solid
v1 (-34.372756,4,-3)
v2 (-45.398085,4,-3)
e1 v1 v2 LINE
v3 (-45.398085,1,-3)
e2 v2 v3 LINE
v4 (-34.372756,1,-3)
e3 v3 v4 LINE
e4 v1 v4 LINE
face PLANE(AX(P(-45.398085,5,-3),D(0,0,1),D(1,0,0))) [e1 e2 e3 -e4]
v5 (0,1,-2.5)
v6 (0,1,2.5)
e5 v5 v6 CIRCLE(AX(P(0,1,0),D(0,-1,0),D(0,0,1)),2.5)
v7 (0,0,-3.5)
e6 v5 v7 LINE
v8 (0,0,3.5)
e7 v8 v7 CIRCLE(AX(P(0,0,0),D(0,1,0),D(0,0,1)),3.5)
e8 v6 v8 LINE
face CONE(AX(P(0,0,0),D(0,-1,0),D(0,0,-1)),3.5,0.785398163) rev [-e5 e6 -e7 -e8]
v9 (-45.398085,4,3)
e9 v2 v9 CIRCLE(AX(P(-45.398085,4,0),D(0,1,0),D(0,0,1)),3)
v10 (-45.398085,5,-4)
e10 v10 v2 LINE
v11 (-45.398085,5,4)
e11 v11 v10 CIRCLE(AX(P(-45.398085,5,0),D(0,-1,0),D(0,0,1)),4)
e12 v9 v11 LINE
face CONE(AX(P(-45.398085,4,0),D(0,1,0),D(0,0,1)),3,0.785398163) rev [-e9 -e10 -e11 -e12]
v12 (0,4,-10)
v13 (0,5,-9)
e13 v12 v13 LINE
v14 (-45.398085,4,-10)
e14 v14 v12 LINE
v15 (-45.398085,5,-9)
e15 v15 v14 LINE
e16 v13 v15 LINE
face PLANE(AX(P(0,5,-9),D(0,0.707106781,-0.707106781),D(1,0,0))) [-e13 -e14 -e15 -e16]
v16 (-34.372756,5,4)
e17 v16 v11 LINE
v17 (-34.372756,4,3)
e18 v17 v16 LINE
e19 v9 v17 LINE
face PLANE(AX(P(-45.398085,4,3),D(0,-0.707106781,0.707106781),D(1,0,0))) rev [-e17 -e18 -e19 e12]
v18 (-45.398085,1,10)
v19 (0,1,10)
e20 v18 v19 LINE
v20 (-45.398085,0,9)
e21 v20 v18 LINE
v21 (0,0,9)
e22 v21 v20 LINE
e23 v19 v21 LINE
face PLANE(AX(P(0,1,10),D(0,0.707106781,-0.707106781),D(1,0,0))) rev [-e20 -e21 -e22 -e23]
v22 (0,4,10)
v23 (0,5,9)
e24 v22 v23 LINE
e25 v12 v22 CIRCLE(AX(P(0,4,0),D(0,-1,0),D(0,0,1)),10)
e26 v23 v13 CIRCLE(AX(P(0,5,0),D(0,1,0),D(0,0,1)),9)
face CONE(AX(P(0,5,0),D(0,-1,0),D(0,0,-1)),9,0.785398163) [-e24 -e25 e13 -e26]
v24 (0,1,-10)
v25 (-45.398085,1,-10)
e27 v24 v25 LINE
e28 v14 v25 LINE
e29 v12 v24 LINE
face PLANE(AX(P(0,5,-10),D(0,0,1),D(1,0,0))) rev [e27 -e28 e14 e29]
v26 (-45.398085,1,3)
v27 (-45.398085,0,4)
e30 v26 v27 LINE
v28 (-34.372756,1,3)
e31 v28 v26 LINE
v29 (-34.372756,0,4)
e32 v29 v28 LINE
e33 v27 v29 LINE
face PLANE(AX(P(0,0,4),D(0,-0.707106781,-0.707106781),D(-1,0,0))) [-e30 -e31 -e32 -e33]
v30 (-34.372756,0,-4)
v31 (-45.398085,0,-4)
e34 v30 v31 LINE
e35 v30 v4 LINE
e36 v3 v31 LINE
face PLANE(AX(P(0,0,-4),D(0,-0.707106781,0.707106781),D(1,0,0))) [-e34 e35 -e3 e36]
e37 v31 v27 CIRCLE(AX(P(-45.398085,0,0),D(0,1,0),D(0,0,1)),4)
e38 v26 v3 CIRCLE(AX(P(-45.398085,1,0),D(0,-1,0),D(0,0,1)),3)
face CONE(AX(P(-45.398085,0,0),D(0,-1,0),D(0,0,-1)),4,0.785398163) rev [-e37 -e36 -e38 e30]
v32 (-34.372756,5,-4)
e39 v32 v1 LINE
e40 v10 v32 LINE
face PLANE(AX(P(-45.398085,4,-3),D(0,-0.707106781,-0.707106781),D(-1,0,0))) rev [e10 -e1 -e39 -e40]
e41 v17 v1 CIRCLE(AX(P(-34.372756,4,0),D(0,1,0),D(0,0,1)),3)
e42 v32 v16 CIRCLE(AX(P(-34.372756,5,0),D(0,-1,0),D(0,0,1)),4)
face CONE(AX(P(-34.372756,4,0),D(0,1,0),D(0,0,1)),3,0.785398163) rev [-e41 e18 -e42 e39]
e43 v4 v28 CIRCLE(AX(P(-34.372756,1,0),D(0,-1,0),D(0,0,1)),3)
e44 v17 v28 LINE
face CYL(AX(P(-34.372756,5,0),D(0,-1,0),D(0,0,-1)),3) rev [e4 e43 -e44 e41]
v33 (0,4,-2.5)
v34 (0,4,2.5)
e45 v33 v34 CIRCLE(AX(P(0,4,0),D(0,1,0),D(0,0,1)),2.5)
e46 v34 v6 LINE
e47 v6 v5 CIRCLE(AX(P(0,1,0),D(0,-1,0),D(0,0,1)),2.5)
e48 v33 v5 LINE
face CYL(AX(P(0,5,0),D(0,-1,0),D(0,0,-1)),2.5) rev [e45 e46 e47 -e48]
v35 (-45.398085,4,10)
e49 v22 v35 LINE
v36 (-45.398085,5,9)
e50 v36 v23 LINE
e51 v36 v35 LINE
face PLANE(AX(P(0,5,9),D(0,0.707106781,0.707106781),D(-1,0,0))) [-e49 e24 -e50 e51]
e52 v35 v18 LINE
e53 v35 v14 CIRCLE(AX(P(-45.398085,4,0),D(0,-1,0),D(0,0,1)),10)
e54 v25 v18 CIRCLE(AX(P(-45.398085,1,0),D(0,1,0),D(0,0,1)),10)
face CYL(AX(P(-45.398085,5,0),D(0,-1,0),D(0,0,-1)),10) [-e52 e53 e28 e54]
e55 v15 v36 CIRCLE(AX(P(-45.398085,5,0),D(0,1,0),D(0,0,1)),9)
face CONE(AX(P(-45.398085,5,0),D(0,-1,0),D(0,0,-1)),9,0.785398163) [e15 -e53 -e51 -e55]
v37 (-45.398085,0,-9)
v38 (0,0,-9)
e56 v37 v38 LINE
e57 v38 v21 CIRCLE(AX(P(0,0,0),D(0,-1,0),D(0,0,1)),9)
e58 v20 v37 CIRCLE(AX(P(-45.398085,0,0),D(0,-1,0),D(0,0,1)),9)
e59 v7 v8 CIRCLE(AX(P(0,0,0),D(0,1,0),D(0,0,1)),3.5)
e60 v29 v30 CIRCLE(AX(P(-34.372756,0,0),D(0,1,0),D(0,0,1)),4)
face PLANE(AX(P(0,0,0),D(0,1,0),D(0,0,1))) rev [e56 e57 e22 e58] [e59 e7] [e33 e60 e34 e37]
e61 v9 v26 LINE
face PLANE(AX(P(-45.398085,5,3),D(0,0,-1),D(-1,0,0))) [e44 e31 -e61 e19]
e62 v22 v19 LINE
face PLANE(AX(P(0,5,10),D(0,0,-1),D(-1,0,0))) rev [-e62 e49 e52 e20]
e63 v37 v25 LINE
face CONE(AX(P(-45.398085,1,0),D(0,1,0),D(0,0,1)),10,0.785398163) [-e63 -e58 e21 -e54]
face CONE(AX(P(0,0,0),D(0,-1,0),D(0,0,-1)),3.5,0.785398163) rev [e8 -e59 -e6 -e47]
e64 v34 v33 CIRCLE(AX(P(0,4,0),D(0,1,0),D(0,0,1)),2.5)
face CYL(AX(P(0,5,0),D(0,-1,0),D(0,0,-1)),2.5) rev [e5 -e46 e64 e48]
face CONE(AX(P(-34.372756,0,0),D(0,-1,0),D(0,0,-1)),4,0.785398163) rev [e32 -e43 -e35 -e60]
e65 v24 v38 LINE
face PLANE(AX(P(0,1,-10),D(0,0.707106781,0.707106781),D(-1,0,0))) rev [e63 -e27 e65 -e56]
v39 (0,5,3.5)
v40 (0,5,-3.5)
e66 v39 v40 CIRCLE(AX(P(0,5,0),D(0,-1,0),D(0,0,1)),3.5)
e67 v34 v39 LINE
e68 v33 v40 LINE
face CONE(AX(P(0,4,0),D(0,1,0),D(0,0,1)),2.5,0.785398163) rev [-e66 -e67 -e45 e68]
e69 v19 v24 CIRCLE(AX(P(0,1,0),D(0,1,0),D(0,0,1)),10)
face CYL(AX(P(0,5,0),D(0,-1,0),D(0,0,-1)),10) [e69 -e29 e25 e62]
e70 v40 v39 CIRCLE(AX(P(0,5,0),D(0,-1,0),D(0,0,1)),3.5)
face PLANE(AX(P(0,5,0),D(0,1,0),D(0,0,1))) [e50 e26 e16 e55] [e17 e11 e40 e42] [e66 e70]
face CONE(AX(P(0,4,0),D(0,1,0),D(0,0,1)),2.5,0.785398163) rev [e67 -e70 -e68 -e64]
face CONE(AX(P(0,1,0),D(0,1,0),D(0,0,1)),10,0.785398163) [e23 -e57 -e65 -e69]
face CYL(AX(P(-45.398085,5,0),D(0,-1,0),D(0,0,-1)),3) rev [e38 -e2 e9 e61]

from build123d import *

# Parameters (mm, degrees)
SKETCH1_R           = 2.5
BOSS_EXTRUDE1_DEPTH = 5
CHAMFER1_SIZE       = 1


with BuildPart() as part:
    # Sketch1 → Boss-Extrude1 (new body)
    with BuildSketch(Plane(origin=(0, 0, 0), x_dir=(1, 0, 0), z_dir=(0, 1, 0))):
        with BuildLine():
            Line((0, -10), (-45.398085341, -10))
            ThreePointArc((-45.398085341, -10), (-55.398085341, 0), (-45.398085341, 10))
            Line((-45.398085341, 10), (0, 10))
            ThreePointArc((0, 10), (10, 0), (0, -10))
        make_face()
        with Locations(Location((0, 0, 0), (0, 0, 270))):
            Circle(SKETCH1_R, mode=Mode.SUBTRACT)
        with BuildLine():
            Line((-45.398085341, 3), (-34.372756479, 3))
            ThreePointArc((-34.372756479, 3), (-31.372756479, 0), (-34.372756479, -3))
            Line((-34.372756479, -3), (-45.398085341, -3))
            ThreePointArc((-45.398085341, -3), (-48.398085341, 0), (-45.398085341, 3))
        make_face(mode=Mode.SUBTRACT)
    extrude(amount=BOSS_EXTRUDE1_DEPTH)

    # Chamfer1
    chamfer1_edges = [part.edges().sort_by_distance(p)[0] for p in [
        (0, 0, -2.5),
        (0, 5, -2.5),
        (-55.398085341, 5, 0),
        (-22.69904267, 5, 10),
        (-48.398085341, 0, 0),
        (-39.88542091, 0, 3),
        (-31.372756479, 0, 0),
        (-39.88542091, 0, -3),
        (-48.398085341, 5, 0),
        (-39.88542091, 5, 3),
        (-31.372756479, 5, 0),
        (-39.88542091, 5, -3),
        (10, 5, 0),
        (-22.69904267, 0, 10),
        (-55.398085341, 0, 0),
        (-22.69904267, 0, -10),
        (10, 0, 0),
        (-22.69904267, 5, -10),
    ]]
    chamfer(chamfer1_edges, length=CHAMFER1_SIZE)


solid = part.part
